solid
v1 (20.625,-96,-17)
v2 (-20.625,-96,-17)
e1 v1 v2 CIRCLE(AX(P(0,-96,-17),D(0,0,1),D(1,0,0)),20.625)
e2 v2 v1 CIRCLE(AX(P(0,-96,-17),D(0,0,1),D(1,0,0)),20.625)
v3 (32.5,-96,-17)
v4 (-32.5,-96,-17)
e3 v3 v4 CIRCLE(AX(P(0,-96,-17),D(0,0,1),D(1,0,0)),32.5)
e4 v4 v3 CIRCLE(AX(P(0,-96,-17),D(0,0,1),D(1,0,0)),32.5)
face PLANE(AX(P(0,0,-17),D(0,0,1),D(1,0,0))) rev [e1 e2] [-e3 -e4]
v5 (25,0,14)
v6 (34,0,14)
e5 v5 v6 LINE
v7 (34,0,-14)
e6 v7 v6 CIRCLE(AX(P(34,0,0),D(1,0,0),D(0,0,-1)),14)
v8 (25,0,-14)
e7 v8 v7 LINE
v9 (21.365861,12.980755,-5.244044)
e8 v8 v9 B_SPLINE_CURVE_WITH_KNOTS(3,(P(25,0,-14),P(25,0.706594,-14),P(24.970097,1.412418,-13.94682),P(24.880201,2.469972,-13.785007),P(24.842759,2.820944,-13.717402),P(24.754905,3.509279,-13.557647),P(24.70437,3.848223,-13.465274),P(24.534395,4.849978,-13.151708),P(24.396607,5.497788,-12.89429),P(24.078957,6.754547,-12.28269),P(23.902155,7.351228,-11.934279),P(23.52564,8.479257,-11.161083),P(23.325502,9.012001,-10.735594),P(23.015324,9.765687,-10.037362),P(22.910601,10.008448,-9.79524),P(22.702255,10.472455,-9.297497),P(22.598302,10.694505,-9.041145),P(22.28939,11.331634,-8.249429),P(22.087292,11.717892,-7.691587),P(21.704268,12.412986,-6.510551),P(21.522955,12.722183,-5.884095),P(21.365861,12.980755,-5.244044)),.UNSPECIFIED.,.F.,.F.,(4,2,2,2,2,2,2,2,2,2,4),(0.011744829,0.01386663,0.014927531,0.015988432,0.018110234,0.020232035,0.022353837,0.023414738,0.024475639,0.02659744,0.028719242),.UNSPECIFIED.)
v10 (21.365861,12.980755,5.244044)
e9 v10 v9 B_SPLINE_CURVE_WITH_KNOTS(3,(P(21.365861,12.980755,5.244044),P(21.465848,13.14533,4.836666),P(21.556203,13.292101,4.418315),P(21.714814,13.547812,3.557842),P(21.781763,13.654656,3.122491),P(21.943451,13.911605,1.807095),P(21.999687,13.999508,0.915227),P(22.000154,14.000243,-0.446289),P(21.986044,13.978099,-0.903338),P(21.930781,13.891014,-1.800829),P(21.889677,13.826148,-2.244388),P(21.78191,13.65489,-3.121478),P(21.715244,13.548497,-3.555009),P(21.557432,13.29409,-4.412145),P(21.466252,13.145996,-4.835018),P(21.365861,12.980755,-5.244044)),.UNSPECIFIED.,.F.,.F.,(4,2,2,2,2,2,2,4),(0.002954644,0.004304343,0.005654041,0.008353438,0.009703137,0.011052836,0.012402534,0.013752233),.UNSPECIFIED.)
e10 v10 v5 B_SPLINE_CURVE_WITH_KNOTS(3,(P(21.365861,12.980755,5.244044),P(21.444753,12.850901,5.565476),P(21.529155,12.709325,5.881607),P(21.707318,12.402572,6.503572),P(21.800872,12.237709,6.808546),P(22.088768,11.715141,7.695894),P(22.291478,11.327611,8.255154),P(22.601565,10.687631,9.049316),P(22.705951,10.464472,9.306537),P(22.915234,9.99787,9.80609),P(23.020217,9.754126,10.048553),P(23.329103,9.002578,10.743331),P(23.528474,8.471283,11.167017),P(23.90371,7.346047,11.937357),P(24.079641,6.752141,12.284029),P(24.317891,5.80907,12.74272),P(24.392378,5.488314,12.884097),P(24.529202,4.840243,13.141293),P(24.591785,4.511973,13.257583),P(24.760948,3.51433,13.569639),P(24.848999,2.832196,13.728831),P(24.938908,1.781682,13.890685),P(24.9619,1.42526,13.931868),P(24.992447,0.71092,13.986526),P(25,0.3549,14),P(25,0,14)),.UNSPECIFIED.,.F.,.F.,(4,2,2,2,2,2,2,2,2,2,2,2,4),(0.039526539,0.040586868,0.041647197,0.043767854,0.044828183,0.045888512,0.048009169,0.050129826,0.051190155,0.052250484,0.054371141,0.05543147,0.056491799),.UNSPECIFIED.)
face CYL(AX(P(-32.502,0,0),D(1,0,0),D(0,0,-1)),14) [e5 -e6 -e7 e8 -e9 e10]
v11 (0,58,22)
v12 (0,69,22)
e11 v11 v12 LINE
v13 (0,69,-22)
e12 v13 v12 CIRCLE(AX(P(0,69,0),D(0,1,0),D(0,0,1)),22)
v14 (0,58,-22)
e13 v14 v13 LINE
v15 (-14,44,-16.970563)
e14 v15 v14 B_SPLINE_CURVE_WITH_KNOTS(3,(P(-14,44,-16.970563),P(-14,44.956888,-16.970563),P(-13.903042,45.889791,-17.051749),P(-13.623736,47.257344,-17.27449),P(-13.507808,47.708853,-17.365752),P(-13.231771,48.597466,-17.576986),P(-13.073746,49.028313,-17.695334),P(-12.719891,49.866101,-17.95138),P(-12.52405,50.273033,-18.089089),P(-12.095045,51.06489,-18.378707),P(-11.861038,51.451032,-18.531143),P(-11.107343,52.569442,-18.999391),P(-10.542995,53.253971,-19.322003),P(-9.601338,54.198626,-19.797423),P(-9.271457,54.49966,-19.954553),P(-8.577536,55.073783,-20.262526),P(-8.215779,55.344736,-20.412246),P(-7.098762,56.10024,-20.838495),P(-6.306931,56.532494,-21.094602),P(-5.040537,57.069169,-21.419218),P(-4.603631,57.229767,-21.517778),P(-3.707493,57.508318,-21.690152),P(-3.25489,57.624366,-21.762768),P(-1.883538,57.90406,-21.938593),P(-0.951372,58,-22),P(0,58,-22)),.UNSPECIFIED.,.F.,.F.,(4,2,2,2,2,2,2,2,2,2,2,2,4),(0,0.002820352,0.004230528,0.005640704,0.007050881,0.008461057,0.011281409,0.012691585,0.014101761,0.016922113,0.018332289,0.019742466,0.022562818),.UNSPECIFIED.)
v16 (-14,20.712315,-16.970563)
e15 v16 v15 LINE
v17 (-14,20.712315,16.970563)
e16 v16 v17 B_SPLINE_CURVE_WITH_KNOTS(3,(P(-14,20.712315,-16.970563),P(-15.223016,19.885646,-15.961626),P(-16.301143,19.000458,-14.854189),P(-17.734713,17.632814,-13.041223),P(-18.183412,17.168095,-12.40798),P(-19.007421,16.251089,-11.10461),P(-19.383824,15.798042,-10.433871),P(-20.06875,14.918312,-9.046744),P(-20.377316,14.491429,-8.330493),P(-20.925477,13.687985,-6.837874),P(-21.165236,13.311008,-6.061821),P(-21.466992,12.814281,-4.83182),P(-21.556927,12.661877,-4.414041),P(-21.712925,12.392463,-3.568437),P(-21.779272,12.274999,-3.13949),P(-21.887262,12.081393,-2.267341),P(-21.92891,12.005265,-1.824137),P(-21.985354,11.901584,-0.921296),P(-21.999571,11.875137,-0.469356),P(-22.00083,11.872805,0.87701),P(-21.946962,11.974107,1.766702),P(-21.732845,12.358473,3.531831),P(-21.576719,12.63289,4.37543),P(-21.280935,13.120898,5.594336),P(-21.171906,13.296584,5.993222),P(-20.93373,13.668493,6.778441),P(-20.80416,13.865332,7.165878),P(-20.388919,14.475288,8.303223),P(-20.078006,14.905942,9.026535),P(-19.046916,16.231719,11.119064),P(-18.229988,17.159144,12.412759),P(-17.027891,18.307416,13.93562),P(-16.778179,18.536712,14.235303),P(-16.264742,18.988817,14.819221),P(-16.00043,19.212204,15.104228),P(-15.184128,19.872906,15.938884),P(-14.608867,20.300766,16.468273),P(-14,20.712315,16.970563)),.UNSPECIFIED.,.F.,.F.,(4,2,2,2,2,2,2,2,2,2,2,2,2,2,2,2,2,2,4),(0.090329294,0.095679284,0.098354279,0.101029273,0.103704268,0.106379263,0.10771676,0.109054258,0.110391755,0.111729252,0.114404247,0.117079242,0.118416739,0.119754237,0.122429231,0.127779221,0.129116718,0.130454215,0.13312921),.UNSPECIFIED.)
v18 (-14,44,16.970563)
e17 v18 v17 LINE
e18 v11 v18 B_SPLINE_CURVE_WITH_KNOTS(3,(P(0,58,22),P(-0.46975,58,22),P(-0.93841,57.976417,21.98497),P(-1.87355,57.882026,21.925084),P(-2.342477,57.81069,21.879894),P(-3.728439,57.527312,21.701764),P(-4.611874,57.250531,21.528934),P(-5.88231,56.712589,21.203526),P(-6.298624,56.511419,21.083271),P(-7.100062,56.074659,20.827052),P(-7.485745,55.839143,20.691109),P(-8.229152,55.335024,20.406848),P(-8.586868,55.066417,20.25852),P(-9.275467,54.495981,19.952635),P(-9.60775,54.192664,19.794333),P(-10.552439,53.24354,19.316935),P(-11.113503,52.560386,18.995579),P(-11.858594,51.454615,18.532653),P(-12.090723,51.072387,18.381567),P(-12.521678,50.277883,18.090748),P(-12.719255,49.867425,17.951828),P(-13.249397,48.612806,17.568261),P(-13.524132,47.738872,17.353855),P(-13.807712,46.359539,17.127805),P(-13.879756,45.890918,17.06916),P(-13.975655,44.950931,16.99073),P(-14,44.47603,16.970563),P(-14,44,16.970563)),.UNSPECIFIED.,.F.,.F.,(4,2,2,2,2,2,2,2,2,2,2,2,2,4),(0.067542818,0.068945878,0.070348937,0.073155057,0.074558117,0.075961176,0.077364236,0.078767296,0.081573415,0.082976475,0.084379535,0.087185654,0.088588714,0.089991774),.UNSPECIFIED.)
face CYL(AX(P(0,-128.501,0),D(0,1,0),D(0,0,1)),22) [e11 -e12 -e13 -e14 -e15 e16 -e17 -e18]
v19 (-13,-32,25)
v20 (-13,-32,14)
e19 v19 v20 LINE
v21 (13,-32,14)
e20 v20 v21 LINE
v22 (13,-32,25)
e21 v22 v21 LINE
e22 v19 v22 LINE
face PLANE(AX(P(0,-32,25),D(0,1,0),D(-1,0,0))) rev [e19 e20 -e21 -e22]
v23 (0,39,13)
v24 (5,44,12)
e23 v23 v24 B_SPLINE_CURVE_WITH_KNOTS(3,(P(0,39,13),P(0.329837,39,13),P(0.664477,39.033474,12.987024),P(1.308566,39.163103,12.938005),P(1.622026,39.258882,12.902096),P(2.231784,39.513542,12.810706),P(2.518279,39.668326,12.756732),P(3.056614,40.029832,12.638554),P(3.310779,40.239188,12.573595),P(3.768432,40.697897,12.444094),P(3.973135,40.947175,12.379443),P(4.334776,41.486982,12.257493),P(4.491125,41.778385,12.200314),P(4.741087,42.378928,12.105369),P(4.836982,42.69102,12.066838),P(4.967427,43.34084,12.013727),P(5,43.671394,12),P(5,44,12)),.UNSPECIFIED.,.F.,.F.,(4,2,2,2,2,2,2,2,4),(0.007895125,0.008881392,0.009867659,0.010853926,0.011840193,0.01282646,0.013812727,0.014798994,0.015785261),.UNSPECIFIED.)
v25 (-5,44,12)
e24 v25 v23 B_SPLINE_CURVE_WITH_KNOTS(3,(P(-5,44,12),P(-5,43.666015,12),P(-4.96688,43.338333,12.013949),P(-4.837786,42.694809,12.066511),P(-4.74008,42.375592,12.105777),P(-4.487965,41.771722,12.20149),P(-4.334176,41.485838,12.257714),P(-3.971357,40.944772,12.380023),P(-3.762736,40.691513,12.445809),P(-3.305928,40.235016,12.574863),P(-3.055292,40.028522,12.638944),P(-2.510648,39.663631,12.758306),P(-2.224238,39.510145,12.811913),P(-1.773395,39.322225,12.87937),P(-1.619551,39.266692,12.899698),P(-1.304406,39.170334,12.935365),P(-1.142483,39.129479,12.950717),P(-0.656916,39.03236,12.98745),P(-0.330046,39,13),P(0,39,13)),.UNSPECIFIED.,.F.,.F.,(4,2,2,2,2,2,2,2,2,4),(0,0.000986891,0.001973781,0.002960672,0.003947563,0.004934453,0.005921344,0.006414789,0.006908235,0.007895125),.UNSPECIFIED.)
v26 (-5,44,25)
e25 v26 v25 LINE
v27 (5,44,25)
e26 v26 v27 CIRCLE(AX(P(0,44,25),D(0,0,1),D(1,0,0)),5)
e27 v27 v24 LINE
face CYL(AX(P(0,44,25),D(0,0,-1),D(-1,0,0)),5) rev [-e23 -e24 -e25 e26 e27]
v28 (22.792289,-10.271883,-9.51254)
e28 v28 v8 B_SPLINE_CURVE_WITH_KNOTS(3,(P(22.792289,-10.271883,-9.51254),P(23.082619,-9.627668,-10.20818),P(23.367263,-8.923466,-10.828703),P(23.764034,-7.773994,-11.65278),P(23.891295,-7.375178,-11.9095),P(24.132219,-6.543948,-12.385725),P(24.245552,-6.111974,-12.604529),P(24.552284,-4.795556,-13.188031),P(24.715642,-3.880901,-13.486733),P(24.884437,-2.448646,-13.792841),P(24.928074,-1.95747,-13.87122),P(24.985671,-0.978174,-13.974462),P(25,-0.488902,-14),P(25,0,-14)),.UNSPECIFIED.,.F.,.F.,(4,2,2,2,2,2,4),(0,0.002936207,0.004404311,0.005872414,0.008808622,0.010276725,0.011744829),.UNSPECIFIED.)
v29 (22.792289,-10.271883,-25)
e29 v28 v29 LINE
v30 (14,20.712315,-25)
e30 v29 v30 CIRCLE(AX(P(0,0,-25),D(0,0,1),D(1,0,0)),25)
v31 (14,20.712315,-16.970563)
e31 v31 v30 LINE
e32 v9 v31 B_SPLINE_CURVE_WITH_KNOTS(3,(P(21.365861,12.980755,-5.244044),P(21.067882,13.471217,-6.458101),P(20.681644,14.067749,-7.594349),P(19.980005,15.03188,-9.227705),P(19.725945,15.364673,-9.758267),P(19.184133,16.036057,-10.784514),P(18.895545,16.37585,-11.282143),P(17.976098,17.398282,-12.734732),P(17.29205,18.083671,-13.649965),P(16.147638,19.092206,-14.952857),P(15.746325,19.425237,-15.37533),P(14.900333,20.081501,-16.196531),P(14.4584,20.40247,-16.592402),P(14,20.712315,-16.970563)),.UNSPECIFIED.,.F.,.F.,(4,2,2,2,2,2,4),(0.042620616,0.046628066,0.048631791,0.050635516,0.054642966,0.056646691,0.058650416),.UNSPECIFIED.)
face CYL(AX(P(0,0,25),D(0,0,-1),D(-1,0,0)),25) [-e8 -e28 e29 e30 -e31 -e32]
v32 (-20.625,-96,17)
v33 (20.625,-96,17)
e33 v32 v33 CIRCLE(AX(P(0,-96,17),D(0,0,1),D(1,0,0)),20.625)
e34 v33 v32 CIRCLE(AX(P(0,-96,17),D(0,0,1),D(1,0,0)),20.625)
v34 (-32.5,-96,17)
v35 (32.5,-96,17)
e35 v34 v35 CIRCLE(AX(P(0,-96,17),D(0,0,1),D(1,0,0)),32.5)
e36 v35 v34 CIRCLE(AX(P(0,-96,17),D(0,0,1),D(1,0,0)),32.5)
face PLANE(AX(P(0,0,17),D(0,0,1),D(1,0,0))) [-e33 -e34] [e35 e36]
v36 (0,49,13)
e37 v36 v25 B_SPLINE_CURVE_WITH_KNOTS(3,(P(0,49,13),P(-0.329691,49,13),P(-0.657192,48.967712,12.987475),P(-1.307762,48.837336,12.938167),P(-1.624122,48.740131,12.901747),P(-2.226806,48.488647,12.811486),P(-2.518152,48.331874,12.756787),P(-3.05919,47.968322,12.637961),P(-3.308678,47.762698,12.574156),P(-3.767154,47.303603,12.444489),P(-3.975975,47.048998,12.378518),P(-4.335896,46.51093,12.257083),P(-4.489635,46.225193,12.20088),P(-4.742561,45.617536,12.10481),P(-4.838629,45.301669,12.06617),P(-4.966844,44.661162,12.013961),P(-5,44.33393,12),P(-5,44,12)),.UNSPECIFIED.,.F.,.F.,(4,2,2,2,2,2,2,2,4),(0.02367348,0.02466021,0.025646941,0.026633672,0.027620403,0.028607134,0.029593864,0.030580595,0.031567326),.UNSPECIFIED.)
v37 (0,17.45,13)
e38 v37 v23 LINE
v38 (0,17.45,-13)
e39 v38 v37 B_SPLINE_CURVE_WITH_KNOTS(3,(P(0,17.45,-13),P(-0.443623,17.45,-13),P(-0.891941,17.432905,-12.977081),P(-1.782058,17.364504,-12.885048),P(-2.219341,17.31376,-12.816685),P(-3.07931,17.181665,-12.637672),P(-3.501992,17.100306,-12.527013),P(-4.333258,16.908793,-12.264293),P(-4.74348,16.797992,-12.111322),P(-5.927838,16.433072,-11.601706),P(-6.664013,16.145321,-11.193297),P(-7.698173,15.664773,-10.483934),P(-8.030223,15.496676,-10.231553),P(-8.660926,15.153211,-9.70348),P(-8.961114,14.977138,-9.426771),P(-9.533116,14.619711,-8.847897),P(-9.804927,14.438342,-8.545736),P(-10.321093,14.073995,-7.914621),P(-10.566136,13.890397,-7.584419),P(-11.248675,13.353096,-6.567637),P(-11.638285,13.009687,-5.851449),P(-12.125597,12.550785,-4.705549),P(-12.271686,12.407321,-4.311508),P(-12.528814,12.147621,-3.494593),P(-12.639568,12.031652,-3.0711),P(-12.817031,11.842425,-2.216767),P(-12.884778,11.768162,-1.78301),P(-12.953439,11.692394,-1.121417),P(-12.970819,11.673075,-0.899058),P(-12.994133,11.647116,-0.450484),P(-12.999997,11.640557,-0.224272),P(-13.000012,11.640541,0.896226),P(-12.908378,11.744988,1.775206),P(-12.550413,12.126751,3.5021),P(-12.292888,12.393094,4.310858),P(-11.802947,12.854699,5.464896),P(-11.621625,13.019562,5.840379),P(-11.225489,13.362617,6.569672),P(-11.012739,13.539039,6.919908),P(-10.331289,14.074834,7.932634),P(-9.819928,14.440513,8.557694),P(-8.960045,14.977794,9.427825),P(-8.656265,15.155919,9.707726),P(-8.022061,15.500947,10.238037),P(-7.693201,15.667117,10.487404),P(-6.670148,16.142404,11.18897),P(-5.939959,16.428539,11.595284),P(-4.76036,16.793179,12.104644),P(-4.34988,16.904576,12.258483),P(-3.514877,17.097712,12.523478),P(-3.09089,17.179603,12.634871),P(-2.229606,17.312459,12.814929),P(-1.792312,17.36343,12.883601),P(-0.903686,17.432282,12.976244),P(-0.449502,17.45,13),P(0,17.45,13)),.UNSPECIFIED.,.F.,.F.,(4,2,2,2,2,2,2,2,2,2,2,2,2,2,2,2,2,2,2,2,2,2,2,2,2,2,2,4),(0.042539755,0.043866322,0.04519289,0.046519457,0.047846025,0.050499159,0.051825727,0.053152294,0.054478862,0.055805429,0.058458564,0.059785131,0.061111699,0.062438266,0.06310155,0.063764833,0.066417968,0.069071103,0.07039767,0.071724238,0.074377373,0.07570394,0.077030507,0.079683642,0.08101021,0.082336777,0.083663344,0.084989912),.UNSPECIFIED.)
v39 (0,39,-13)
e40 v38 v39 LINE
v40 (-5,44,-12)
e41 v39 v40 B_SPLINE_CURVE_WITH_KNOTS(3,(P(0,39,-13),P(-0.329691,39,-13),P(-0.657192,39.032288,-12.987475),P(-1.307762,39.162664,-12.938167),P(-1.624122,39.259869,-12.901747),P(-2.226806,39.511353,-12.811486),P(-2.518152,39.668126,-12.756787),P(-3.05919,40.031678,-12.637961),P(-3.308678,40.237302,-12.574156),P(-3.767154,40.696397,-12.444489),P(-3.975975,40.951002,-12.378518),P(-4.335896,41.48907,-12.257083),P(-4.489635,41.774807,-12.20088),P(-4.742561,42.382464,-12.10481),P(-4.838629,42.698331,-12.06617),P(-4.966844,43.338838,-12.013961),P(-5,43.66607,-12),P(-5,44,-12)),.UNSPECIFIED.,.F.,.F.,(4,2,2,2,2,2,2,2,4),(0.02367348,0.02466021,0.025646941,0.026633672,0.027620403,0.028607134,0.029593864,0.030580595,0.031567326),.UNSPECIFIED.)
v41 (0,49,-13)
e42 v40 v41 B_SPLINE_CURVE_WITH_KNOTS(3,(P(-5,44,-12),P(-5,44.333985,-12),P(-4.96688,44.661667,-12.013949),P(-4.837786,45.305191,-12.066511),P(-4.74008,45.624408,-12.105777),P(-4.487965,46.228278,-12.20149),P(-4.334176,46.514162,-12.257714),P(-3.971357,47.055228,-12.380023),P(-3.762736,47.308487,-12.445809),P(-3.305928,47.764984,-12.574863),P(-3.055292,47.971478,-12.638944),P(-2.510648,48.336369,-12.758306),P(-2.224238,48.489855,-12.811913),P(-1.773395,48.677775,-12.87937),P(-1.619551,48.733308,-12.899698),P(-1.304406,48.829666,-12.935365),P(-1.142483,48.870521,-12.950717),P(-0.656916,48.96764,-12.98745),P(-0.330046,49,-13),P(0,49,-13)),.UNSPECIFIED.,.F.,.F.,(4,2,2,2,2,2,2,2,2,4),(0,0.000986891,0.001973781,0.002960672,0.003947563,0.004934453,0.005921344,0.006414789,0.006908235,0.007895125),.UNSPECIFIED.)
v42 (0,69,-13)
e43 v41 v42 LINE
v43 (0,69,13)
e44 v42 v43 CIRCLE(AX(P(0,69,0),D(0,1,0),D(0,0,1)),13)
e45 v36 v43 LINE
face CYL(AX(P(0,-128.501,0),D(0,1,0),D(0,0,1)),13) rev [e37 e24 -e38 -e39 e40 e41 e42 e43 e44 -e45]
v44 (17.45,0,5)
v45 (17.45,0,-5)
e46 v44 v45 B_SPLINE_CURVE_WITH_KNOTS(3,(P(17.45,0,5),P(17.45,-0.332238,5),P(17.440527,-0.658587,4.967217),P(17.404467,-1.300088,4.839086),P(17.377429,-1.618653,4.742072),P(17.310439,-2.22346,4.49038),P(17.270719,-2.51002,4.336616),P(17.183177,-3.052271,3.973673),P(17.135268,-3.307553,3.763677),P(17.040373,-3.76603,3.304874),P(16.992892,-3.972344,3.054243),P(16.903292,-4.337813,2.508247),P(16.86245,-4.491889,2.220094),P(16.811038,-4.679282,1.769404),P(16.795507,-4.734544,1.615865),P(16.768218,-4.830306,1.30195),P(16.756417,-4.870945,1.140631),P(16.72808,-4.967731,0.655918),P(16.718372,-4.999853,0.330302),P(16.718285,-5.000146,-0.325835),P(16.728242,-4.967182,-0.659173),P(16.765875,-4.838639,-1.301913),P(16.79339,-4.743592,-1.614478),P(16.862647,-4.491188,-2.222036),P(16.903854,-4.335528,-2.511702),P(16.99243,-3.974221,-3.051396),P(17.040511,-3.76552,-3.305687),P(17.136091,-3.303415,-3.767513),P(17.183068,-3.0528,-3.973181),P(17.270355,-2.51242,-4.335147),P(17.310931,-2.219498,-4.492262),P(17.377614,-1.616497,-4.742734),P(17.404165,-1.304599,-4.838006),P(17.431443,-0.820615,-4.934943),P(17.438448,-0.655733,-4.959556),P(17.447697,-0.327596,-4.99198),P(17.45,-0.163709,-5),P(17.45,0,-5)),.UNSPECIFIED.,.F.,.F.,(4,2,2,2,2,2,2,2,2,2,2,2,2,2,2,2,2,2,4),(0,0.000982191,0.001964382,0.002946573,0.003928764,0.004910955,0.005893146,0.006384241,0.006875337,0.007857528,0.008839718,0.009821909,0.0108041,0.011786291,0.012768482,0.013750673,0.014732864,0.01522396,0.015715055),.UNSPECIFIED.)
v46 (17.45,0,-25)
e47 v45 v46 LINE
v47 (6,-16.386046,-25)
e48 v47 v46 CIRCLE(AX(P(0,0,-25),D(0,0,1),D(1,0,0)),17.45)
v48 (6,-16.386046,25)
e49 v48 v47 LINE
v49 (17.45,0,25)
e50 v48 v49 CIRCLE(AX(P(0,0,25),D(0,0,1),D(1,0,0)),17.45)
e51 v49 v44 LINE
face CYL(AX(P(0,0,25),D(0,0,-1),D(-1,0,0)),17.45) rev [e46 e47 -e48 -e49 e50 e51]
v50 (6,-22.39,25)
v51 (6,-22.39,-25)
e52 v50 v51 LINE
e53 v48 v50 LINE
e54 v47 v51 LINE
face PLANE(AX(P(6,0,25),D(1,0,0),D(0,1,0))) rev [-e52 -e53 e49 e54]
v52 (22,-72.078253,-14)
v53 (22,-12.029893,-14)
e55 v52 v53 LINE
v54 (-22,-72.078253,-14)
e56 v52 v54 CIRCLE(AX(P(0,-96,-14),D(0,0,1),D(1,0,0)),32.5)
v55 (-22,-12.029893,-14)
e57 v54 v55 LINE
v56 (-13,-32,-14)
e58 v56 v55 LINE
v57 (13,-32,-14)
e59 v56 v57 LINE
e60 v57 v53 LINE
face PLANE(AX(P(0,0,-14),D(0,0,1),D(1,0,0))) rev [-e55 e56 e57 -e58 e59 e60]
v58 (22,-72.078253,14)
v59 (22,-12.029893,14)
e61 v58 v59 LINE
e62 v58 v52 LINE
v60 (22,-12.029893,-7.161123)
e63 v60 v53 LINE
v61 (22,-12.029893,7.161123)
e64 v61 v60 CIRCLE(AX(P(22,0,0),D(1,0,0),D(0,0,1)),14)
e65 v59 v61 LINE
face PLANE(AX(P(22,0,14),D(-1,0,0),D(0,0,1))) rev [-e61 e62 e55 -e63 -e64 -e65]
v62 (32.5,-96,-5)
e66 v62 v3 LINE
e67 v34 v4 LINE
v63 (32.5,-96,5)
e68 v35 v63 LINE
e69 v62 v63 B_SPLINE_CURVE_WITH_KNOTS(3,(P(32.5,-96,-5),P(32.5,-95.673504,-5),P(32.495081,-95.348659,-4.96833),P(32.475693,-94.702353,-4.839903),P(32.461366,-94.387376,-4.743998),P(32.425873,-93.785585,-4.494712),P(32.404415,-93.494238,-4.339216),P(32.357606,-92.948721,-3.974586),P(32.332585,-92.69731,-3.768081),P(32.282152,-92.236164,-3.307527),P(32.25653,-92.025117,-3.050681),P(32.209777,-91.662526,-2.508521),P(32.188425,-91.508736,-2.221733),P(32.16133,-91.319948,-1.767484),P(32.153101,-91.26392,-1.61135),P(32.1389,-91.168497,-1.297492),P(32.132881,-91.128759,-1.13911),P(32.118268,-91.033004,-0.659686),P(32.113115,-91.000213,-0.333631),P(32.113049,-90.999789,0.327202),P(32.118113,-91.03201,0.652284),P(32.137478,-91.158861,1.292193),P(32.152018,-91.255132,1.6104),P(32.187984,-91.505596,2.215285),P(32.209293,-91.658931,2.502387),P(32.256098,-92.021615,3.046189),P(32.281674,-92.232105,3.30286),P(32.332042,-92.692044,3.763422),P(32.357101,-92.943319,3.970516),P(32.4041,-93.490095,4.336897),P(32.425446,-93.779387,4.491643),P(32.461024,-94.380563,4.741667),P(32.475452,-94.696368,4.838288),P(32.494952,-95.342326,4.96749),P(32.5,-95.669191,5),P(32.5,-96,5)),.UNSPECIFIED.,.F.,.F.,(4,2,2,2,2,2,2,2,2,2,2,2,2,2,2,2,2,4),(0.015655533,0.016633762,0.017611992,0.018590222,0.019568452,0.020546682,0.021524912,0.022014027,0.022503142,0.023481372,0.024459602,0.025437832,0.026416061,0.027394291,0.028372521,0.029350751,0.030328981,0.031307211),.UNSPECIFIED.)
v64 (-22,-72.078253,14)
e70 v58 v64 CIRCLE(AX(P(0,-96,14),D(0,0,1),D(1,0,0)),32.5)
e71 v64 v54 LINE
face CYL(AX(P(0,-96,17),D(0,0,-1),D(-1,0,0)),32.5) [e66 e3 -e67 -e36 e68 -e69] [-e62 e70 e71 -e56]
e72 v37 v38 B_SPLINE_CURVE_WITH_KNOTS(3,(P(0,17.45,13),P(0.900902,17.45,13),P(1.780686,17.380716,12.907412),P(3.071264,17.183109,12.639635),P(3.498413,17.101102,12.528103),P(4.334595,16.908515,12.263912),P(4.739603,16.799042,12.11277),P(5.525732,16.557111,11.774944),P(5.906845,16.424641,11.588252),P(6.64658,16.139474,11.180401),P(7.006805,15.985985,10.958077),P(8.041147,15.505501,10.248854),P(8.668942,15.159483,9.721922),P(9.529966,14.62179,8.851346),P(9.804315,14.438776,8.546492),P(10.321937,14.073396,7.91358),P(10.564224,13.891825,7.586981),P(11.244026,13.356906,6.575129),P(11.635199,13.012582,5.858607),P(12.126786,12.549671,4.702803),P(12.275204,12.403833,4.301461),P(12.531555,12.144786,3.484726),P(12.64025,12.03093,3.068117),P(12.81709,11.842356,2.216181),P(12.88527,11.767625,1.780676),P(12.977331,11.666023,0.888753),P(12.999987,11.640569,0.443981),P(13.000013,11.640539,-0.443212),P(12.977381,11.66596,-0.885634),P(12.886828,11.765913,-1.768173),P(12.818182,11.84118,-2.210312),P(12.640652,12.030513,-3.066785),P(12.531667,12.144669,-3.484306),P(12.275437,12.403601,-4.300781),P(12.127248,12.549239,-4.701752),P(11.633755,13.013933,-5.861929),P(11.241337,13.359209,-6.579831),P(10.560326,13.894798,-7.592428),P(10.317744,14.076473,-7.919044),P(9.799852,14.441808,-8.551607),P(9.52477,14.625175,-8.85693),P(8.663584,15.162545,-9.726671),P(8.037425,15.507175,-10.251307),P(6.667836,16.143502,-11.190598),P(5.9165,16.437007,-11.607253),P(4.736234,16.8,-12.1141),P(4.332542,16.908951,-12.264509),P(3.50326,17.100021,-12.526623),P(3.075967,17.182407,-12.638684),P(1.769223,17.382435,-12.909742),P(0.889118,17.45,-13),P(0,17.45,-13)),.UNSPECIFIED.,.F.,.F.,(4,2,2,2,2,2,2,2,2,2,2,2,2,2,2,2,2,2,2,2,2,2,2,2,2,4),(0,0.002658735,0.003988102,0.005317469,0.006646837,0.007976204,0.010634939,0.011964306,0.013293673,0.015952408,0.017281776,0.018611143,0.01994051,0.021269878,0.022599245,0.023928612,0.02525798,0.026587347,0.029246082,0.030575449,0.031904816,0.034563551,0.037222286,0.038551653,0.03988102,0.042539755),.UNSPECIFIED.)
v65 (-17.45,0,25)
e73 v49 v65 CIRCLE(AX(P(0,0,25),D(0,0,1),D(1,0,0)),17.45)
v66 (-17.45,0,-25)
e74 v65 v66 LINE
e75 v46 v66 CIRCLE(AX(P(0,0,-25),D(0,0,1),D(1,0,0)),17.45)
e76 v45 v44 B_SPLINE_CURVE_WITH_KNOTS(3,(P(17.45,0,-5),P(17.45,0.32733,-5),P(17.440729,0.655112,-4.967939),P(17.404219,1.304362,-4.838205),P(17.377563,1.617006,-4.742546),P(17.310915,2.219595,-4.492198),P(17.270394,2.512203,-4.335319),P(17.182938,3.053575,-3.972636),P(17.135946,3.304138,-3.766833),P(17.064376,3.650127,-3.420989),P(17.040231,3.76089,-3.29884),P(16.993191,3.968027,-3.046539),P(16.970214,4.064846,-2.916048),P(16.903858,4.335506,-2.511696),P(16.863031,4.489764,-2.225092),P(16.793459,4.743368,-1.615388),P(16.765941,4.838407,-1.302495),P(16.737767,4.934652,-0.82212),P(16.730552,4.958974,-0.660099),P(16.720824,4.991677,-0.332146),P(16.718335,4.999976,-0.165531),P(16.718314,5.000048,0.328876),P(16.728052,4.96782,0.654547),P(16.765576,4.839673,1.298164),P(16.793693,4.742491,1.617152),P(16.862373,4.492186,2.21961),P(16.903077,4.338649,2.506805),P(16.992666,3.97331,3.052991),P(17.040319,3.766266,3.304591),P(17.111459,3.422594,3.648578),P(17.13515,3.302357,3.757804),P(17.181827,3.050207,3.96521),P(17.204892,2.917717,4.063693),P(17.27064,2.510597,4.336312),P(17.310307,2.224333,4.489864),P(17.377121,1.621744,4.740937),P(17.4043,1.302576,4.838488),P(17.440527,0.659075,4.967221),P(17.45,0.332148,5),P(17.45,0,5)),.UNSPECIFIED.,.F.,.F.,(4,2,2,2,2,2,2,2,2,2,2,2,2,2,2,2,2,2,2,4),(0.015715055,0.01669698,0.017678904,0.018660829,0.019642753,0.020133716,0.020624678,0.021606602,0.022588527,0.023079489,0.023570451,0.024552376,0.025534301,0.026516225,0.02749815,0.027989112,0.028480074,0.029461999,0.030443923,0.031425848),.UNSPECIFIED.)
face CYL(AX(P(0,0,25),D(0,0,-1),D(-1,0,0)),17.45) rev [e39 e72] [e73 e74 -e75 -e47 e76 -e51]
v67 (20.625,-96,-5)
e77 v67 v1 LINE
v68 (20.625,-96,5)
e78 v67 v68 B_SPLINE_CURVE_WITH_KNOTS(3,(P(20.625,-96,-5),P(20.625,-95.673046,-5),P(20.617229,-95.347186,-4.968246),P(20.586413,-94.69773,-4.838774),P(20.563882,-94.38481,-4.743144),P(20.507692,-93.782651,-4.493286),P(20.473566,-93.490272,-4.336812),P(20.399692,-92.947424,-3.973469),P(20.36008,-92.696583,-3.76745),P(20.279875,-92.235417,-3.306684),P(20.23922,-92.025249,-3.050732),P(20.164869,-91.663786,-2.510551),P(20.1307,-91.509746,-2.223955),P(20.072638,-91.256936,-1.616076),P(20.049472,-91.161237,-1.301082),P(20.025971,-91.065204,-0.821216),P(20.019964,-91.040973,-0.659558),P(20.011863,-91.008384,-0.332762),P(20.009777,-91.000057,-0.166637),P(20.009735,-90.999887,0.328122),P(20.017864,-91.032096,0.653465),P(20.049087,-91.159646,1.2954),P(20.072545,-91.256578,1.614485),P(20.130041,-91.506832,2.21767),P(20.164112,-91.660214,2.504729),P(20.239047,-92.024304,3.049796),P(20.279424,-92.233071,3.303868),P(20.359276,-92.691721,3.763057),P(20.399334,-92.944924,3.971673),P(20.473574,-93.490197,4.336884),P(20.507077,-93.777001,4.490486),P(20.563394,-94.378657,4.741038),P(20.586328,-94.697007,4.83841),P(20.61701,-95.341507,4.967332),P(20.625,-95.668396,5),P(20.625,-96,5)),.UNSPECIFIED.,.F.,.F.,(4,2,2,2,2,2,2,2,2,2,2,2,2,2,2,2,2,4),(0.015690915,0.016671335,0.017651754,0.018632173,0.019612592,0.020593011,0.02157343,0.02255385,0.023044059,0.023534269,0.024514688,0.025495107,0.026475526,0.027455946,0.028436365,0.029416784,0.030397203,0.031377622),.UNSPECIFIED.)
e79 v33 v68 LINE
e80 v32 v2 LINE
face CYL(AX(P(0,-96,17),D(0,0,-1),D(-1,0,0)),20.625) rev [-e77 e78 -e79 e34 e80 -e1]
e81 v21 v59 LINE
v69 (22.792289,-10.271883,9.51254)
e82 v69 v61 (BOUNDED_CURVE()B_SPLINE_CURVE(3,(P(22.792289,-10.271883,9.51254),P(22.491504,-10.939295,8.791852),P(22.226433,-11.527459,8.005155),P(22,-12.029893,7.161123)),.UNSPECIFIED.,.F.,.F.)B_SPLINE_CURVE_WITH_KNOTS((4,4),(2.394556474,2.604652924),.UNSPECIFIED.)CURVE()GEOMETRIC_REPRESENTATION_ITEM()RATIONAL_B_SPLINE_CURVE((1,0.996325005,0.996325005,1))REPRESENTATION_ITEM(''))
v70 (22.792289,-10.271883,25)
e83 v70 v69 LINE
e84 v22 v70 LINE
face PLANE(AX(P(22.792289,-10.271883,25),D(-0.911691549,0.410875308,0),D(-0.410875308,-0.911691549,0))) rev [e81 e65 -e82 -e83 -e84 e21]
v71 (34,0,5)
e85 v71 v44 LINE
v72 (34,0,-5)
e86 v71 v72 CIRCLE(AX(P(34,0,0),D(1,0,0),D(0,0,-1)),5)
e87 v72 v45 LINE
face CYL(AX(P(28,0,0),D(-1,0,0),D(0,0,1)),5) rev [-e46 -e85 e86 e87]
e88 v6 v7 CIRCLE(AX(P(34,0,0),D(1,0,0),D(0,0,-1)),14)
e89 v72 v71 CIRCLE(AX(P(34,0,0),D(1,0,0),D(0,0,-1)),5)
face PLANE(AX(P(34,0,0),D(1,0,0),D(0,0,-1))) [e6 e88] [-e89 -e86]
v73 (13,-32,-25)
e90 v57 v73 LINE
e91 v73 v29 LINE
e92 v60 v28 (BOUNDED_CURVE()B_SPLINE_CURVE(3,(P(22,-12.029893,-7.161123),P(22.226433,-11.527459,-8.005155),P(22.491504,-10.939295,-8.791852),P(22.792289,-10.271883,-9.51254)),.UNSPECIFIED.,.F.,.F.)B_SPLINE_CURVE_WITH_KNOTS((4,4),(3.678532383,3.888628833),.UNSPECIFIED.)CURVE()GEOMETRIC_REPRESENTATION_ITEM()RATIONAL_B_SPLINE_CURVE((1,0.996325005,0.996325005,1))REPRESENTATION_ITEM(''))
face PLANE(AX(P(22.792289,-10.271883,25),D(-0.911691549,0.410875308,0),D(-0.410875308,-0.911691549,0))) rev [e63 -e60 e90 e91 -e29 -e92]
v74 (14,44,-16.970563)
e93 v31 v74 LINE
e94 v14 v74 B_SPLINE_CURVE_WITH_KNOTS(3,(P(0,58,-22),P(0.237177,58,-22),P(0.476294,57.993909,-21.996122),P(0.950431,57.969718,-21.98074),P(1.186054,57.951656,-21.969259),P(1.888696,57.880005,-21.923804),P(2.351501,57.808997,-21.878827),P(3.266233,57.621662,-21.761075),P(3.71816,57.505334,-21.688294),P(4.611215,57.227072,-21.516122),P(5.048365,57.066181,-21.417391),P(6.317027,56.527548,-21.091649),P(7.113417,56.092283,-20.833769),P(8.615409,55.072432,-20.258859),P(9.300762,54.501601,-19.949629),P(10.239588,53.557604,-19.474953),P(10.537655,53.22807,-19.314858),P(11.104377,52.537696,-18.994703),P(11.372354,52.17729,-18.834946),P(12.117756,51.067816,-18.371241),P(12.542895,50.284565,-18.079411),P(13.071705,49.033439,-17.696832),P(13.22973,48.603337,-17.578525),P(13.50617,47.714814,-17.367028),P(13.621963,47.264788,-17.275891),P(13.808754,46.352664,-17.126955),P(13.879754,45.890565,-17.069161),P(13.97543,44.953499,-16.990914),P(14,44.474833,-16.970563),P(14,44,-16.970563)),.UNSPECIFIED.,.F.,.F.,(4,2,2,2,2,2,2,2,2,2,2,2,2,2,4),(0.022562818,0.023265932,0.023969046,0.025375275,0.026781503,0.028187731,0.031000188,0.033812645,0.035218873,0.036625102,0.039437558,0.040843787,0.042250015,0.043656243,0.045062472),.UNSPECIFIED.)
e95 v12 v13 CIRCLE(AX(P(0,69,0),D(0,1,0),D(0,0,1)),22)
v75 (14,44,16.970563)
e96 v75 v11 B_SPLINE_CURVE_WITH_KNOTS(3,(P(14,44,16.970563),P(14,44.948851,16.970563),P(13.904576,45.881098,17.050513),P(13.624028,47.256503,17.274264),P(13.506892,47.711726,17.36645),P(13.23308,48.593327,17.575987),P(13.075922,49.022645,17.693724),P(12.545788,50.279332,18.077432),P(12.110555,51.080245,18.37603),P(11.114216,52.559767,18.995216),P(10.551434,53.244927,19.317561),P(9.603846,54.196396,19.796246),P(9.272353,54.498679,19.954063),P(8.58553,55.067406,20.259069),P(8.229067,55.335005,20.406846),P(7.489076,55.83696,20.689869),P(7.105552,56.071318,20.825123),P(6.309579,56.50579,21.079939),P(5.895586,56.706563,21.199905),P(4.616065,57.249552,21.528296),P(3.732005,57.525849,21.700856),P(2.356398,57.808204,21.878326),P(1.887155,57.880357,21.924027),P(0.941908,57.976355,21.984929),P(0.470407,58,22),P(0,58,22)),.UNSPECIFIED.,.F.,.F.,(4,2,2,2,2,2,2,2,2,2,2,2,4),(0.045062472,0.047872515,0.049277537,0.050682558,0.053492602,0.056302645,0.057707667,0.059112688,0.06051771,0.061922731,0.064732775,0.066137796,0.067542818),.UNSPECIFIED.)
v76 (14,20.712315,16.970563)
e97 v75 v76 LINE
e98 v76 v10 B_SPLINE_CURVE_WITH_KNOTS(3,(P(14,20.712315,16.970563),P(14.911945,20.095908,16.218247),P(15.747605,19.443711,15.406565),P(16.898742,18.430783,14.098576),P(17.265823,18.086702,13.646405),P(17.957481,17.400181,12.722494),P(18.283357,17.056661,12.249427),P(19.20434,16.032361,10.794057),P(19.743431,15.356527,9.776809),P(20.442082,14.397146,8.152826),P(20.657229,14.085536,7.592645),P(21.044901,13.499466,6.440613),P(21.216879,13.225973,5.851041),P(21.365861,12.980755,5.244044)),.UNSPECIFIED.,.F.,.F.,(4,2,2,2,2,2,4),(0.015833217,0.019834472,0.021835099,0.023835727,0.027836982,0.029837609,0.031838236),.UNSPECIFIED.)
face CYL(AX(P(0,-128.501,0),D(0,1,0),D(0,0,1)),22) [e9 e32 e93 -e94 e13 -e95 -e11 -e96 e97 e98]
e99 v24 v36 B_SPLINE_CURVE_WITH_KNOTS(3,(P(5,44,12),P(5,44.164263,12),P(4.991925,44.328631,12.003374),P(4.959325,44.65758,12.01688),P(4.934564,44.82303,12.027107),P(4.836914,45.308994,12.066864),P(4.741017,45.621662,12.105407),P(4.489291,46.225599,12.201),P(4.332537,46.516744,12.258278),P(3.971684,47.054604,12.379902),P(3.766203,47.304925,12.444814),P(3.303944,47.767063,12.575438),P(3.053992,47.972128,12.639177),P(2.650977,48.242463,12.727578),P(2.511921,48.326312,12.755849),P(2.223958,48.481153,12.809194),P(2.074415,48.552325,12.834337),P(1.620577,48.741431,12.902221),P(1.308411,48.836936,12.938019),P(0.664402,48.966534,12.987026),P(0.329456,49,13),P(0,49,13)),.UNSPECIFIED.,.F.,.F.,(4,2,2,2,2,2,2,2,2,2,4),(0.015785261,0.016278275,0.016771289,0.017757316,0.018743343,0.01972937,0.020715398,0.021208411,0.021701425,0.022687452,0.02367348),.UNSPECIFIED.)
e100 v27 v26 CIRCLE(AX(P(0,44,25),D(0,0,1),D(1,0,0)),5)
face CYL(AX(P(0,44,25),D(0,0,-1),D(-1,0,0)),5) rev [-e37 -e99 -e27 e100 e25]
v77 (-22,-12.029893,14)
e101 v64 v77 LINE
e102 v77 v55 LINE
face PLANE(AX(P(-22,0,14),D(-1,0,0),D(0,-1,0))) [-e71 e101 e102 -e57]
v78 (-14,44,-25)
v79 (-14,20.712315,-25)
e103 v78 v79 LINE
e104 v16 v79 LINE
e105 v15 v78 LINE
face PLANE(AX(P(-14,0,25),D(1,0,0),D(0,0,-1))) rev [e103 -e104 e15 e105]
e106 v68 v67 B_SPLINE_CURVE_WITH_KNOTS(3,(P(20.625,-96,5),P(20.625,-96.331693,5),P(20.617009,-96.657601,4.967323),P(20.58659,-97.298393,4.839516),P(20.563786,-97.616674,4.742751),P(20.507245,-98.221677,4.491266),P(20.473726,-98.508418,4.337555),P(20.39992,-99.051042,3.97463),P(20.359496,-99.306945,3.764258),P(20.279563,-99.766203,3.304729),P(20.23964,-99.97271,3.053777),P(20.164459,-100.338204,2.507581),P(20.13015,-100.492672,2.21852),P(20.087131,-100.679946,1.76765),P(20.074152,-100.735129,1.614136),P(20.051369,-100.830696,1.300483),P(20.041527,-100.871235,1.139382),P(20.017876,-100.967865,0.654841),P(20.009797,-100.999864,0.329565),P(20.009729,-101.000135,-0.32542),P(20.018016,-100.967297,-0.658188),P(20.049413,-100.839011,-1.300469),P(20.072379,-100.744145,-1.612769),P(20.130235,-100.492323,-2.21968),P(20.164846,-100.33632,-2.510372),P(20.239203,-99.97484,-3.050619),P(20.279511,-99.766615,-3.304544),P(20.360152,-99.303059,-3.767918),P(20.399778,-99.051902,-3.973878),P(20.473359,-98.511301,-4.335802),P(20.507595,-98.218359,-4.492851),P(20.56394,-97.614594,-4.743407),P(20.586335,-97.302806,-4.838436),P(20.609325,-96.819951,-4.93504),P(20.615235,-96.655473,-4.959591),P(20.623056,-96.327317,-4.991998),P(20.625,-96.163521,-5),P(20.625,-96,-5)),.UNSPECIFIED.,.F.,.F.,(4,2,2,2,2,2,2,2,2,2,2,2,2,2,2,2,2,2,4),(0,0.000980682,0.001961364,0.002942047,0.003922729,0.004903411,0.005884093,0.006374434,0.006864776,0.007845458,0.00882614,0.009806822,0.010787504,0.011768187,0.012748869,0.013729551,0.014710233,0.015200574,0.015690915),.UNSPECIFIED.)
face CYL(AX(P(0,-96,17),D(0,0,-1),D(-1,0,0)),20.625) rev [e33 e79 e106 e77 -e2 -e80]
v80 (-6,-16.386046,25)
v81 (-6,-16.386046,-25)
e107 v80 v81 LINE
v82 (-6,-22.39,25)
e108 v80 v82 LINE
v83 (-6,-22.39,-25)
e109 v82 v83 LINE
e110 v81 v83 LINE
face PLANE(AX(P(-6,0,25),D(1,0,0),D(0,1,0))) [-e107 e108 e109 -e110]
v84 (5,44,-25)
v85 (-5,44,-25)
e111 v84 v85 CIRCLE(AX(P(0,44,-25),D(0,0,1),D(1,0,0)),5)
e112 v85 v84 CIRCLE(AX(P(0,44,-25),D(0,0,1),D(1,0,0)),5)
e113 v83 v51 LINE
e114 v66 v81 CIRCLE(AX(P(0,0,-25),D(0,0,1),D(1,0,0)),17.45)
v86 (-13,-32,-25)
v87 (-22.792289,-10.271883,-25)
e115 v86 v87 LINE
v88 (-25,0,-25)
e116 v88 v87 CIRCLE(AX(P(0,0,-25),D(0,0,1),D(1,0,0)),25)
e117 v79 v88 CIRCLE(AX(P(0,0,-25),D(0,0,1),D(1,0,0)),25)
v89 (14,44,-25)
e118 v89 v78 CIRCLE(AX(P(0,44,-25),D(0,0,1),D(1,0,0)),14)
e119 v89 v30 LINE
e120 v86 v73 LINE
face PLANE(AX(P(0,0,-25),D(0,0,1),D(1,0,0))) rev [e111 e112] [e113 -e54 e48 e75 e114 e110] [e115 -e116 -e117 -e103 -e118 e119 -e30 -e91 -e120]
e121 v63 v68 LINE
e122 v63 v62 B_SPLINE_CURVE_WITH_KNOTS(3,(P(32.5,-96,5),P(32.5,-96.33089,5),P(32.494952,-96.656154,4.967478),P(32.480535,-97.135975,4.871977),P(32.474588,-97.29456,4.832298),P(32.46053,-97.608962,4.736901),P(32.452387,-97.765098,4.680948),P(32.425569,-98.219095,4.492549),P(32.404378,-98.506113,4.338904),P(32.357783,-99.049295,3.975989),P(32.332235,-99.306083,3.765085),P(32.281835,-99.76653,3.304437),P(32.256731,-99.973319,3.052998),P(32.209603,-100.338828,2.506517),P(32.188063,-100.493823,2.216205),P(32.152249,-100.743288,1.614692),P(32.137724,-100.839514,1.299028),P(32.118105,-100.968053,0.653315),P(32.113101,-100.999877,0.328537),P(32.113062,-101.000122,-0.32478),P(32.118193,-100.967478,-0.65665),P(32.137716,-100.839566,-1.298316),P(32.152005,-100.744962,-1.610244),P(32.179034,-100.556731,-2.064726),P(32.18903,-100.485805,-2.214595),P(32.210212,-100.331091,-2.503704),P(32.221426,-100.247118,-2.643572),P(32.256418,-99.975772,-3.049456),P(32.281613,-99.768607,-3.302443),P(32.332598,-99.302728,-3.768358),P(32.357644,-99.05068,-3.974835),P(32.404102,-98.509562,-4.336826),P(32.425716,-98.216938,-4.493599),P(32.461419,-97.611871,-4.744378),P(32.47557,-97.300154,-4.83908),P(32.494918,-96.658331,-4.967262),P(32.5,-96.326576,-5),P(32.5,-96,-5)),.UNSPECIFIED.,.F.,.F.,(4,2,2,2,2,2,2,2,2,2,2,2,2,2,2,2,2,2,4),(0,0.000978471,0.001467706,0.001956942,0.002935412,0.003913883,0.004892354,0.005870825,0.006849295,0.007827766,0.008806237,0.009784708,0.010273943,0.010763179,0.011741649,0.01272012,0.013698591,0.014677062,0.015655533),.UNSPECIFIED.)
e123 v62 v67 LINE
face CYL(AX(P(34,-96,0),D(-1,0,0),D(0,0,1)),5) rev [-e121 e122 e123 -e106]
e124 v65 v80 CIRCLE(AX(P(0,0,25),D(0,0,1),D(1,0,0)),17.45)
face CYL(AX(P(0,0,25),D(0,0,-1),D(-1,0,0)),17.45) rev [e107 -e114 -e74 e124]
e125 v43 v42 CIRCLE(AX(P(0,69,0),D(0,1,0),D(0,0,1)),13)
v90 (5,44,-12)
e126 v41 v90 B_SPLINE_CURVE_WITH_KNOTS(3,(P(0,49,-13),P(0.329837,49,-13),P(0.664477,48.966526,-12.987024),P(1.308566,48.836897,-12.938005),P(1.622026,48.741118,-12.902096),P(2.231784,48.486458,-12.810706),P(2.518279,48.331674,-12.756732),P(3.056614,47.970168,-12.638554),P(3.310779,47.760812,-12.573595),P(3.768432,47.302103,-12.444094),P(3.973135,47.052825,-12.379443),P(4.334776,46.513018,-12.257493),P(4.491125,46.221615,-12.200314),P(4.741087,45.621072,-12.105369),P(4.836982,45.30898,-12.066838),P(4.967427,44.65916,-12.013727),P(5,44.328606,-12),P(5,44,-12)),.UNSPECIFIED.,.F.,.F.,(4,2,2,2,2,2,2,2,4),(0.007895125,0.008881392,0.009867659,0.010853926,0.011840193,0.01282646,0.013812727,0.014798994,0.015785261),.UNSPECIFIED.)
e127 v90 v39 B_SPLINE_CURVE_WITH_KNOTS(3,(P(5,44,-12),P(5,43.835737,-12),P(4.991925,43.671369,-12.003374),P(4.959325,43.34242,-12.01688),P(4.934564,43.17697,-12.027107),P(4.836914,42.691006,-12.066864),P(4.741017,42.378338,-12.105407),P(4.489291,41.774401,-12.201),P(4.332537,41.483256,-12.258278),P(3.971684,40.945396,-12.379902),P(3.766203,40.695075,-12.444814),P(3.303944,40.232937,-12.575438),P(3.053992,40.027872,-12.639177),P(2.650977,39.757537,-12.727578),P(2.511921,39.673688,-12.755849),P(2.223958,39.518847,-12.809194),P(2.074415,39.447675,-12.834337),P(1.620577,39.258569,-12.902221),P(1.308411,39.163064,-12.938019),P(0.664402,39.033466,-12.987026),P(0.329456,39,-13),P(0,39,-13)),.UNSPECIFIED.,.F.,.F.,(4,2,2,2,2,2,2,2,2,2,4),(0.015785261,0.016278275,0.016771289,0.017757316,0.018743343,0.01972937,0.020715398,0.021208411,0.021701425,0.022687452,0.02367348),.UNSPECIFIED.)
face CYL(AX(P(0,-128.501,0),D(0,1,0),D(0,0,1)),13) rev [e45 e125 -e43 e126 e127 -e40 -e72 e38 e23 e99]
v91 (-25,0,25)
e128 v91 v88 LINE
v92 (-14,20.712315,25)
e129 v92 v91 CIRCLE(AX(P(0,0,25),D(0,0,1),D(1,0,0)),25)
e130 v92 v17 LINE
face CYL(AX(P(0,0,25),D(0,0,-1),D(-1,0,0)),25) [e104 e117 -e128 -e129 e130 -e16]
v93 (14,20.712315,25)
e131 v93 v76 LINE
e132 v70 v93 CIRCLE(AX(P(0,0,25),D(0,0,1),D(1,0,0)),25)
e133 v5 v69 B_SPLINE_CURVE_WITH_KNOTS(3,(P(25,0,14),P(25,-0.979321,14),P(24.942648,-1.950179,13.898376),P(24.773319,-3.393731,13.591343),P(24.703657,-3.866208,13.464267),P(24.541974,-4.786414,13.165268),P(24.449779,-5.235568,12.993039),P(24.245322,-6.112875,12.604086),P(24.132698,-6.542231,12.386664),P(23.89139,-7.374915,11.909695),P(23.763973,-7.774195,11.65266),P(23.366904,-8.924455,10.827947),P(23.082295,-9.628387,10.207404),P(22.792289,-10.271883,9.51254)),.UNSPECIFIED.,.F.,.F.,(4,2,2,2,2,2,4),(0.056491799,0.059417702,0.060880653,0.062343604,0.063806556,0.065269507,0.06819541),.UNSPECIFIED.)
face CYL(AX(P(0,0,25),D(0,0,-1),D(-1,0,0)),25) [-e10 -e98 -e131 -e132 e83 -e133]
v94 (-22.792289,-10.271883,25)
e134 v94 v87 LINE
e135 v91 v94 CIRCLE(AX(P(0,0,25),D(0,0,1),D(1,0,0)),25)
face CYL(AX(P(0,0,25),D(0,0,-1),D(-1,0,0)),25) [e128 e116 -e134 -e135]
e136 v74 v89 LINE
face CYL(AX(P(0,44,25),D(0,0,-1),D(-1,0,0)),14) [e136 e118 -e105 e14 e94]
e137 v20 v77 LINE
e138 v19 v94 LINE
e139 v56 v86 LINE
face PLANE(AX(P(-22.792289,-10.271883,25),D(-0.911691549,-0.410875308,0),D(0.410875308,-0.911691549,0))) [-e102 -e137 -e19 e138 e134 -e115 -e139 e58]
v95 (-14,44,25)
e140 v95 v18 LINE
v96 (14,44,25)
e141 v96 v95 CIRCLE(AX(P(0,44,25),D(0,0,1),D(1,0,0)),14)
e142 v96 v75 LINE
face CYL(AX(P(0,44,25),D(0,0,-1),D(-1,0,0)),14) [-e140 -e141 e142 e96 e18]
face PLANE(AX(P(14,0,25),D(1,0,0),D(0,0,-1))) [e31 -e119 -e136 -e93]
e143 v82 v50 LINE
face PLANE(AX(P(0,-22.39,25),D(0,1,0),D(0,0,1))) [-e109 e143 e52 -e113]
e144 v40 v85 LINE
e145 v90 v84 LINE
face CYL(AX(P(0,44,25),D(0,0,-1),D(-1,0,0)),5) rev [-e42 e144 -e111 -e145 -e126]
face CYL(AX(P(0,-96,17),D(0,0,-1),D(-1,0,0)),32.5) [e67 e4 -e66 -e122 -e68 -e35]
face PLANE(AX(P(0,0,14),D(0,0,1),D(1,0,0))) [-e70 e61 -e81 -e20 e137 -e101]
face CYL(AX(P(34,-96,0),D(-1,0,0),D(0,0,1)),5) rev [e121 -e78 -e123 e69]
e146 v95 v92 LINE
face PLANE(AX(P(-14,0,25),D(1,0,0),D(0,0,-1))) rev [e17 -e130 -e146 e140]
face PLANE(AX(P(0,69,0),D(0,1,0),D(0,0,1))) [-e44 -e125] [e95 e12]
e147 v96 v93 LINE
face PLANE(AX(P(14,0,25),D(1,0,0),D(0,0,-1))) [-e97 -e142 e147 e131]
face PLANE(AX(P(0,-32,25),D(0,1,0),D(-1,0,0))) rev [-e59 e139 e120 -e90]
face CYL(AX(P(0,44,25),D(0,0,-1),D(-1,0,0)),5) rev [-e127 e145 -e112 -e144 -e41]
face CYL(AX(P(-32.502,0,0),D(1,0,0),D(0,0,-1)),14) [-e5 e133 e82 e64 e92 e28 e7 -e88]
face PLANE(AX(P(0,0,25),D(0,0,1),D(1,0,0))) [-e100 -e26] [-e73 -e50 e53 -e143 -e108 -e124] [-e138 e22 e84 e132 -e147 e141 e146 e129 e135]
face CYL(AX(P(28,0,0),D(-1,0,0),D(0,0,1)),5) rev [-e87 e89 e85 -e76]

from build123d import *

# Parameters (mm, degrees)
LINK_ARM_PROFILE_SKETCH_R    = 5
MAIN_ARM_BODY_50MM_DEPTH     = 25
SKETCH1_3_R                  = 32.5
SKETCH1_3_R_2                = 20.625
ARM_WEB_34MM_DEPTH           = 17
LUG_PLATE_28MM_DEPTH         = 14
UPPER_CROSS_HOLE_10_SKETCH_R = 5
UPPER_CROSS_HOLE_10_DEPTH    = 28
SIDE_BOSS_REACH              = 148.832
SIDE_BOSS_SKETCH_R           = 14
SIDE_BOSS_SKETCH_R_2         = 5
LOWER_CROSS_HOLE_10_SKETCH_R = 5
LOWER_CROSS_HOLE_10_DEPTH    = 136.252541609
TOP_BOSS_44_REACH            = 203.959
TOP_BOSS_44_END_RADIUS       = 25
TOP_BOSS_44_SKETCH_R         = 22
LUG_HOLE_10_SKETCH_R         = 5
LUG_HOLE_10_DEPTH            = 143.01496415
TOP_BORE_26_REACH            = 203.959
TOP_BORE_26_END_RADIUS       = 17.45
TOP_BORE_26_SKETCH_R         = 13


with BuildPart() as part:
    # Link Arm Profile Sketch → Main Arm Body 50mm (new, symmetric)
    # profile 1 of 2: a face of its own
    with BuildSketch(Plane.XY):
        with BuildLine():
            Line((-14, 44), (-14, 20.712315177))
            ThreePointArc((-14, 20.712315177), (0, 25), (14, 20.712315177))
            Line((14, 20.712315177), (14, 44))
            ThreePointArc((14, 44), (0, 58), (-14, 44))
        make_face()
        with Locations((0, 44)):
            Circle(LINK_ARM_PROFILE_SKETCH_R, mode=Mode.SUBTRACT)
    # profile 2 of 2: a face of its own
    with BuildSketch(Plane.XY):
        with BuildLine():
            ThreePointArc((22.792288735, -10.271882702), (0, 25), (-22.792288735, -10.271882702))
            Line((-22.792288735, -10.271882702), (-13, -32))
            Line((-13, -32), (13, -32))
            Line((13, -32), (22.792288735, -10.271882702))
        make_face()
        with BuildLine():
            ThreePointArc((6, -16.386045893), (0, 17.45), (-6, -16.386045893))
            Line((-6, -16.386045893), (-6, -22.39))
            Line((-6, -22.39), (6, -22.39))
            Line((6, -22.39), (6, -16.386045893))
        make_face(mode=Mode.SUBTRACT)
    extrude(amount=MAIN_ARM_BODY_50MM_DEPTH, both=True)



with BuildPart() as body_2:
    # Sketch1_3 → Arm Web 34mm (new, symmetric)
    with BuildSketch(Plane.XY):
        with Locations((0, -96)):
            Circle(SKETCH1_3_R)
        with Locations((0, -96)):
            Circle(SKETCH1_3_R_2, mode=Mode.SUBTRACT)
    extrude(amount=ARM_WEB_34MM_DEPTH, both=True)


with BuildPart() as part_1:
    add(part.part)

    add(body_2.part)  # Lug Plate 28mm merges body 2
    # Sketch1_5 → Lug Plate 28mm (add, symmetric)
    with BuildSketch(Plane.XY):
        with BuildLine():
            Line((13, -32), (-13, -32))
            Line((-13, -32), (-22, -12.029892808))
            Line((-22, -12.029892808), (-22, -72.078252572))
            ThreePointArc((-22, -72.078252572), (0, -63.5), (22, -72.078252572))
            Line((22, -72.078252572), (22, -12.029892808))
            Line((22, -12.029892808), (13, -32))
        make_face()
    extrude(amount=LUG_PLATE_28MM_DEPTH, both=True)

    # Upper Cross Hole _10 Sketch → Upper Cross Hole _10 (cut)
    with BuildSketch(Plane(origin=(0, 0, 0), x_dir=(0, 0, -1), z_dir=(1, 0, 0))):
        with Locations(Location((0, 0, 0), (0, 0, 180))):
            Circle(UPPER_CROSS_HOLE_10_SKETCH_R)
    extrude(amount=UPPER_CROSS_HOLE_10_DEPTH, mode=Mode.SUBTRACT)

    # Side Boss Sketch → Side Boss (add, up to next)
    with BuildSketch(Plane(origin=(34, 0, 0), x_dir=(0, 0, -1), z_dir=(1, 0, 0)), mode=Mode.PRIVATE) as side_boss_sk1:
        Circle(SIDE_BOSS_SKETCH_R)
        with Locations(Location((0, 0, 0), (0, 0, 180))):
            Circle(SIDE_BOSS_SKETCH_R_2, mode=Mode.SUBTRACT)
    side_boss_tool1 = extrude(side_boss_sk1.sketch, amount=-SIDE_BOSS_REACH, mode=Mode.PRIVATE) - part_1.part
    add(side_boss_tool1.solids().sort_by_distance((34, 0, 13.60402))[0])

    # Lower Cross Hole _10 Sketch → Lower Cross Hole _10 (cut, through all)
    with BuildSketch(Plane(origin=(0, 0, 0), x_dir=(0, 0, -1), z_dir=(1, 0, 0))):
        with Locations(Location((0, -96, 0), (0, 0, 180))):
            Circle(LOWER_CROSS_HOLE_10_SKETCH_R)
    extrude(amount=LOWER_CROSS_HOLE_10_DEPTH, mode=Mode.SUBTRACT)

    # Top Boss _44: up to this cylinder (the profile starts outside it)
    top_boss_44_end = Plane(origin=(0, 0, 0), z_dir=(0, 0, -1)) * Cylinder(TOP_BOSS_44_END_RADIUS, 458.918, mode=Mode.PRIVATE)
    # Top Boss _44 Sketch → Top Boss _44 (add, up to the surface)
    with BuildSketch(Plane(origin=(0, 69, 0), x_dir=(1, 0, 0), z_dir=(0, 1, 0)), mode=Mode.PRIVATE) as top_boss_44_sk1:
        with Locations(Location((0, 0, 0), (0, 0, 270))):
            Circle(TOP_BOSS_44_SKETCH_R)
    top_boss_44_tool1 = extrude(top_boss_44_sk1.sketch, amount=-TOP_BOSS_44_REACH, mode=Mode.PRIVATE) - top_boss_44_end
    add(top_boss_44_tool1.solids().sort_by_distance((0, 69, 0))[0])

    # Lug Hole _10 Sketch → Lug Hole _10 (cut, through all)
    with BuildSketch(Plane.XY.offset(25)):
        with Locations((0, 44)):
            Circle(LUG_HOLE_10_SKETCH_R)
    extrude(amount=-LUG_HOLE_10_DEPTH, mode=Mode.SUBTRACT)

    # Top Bore _26: up to this cylinder (the profile starts outside it)
    top_bore_26_end = Plane(origin=(0, 0, 0), z_dir=(0, 0, -1)) * Cylinder(TOP_BORE_26_END_RADIUS, 443.818, mode=Mode.PRIVATE)
    # Top Bore _26 Sketch → Top Bore _26 (cut, up to the surface)
    with BuildSketch(Plane(origin=(0, 69, 0), x_dir=(1, 0, 0), z_dir=(0, 1, 0)), mode=Mode.PRIVATE) as top_bore_26_sk1:
        with Locations(Location((0, 0, 0), (0, 0, 270))):
            Circle(TOP_BORE_26_SKETCH_R)
    top_bore_26_tool1 = extrude(top_bore_26_sk1.sketch, amount=-TOP_BORE_26_REACH, mode=Mode.PRIVATE) - top_bore_26_end
    add(top_bore_26_tool1.solids().sort_by_distance((0, 69, 0))[0], mode=Mode.SUBTRACT)


solid = part_1.part
